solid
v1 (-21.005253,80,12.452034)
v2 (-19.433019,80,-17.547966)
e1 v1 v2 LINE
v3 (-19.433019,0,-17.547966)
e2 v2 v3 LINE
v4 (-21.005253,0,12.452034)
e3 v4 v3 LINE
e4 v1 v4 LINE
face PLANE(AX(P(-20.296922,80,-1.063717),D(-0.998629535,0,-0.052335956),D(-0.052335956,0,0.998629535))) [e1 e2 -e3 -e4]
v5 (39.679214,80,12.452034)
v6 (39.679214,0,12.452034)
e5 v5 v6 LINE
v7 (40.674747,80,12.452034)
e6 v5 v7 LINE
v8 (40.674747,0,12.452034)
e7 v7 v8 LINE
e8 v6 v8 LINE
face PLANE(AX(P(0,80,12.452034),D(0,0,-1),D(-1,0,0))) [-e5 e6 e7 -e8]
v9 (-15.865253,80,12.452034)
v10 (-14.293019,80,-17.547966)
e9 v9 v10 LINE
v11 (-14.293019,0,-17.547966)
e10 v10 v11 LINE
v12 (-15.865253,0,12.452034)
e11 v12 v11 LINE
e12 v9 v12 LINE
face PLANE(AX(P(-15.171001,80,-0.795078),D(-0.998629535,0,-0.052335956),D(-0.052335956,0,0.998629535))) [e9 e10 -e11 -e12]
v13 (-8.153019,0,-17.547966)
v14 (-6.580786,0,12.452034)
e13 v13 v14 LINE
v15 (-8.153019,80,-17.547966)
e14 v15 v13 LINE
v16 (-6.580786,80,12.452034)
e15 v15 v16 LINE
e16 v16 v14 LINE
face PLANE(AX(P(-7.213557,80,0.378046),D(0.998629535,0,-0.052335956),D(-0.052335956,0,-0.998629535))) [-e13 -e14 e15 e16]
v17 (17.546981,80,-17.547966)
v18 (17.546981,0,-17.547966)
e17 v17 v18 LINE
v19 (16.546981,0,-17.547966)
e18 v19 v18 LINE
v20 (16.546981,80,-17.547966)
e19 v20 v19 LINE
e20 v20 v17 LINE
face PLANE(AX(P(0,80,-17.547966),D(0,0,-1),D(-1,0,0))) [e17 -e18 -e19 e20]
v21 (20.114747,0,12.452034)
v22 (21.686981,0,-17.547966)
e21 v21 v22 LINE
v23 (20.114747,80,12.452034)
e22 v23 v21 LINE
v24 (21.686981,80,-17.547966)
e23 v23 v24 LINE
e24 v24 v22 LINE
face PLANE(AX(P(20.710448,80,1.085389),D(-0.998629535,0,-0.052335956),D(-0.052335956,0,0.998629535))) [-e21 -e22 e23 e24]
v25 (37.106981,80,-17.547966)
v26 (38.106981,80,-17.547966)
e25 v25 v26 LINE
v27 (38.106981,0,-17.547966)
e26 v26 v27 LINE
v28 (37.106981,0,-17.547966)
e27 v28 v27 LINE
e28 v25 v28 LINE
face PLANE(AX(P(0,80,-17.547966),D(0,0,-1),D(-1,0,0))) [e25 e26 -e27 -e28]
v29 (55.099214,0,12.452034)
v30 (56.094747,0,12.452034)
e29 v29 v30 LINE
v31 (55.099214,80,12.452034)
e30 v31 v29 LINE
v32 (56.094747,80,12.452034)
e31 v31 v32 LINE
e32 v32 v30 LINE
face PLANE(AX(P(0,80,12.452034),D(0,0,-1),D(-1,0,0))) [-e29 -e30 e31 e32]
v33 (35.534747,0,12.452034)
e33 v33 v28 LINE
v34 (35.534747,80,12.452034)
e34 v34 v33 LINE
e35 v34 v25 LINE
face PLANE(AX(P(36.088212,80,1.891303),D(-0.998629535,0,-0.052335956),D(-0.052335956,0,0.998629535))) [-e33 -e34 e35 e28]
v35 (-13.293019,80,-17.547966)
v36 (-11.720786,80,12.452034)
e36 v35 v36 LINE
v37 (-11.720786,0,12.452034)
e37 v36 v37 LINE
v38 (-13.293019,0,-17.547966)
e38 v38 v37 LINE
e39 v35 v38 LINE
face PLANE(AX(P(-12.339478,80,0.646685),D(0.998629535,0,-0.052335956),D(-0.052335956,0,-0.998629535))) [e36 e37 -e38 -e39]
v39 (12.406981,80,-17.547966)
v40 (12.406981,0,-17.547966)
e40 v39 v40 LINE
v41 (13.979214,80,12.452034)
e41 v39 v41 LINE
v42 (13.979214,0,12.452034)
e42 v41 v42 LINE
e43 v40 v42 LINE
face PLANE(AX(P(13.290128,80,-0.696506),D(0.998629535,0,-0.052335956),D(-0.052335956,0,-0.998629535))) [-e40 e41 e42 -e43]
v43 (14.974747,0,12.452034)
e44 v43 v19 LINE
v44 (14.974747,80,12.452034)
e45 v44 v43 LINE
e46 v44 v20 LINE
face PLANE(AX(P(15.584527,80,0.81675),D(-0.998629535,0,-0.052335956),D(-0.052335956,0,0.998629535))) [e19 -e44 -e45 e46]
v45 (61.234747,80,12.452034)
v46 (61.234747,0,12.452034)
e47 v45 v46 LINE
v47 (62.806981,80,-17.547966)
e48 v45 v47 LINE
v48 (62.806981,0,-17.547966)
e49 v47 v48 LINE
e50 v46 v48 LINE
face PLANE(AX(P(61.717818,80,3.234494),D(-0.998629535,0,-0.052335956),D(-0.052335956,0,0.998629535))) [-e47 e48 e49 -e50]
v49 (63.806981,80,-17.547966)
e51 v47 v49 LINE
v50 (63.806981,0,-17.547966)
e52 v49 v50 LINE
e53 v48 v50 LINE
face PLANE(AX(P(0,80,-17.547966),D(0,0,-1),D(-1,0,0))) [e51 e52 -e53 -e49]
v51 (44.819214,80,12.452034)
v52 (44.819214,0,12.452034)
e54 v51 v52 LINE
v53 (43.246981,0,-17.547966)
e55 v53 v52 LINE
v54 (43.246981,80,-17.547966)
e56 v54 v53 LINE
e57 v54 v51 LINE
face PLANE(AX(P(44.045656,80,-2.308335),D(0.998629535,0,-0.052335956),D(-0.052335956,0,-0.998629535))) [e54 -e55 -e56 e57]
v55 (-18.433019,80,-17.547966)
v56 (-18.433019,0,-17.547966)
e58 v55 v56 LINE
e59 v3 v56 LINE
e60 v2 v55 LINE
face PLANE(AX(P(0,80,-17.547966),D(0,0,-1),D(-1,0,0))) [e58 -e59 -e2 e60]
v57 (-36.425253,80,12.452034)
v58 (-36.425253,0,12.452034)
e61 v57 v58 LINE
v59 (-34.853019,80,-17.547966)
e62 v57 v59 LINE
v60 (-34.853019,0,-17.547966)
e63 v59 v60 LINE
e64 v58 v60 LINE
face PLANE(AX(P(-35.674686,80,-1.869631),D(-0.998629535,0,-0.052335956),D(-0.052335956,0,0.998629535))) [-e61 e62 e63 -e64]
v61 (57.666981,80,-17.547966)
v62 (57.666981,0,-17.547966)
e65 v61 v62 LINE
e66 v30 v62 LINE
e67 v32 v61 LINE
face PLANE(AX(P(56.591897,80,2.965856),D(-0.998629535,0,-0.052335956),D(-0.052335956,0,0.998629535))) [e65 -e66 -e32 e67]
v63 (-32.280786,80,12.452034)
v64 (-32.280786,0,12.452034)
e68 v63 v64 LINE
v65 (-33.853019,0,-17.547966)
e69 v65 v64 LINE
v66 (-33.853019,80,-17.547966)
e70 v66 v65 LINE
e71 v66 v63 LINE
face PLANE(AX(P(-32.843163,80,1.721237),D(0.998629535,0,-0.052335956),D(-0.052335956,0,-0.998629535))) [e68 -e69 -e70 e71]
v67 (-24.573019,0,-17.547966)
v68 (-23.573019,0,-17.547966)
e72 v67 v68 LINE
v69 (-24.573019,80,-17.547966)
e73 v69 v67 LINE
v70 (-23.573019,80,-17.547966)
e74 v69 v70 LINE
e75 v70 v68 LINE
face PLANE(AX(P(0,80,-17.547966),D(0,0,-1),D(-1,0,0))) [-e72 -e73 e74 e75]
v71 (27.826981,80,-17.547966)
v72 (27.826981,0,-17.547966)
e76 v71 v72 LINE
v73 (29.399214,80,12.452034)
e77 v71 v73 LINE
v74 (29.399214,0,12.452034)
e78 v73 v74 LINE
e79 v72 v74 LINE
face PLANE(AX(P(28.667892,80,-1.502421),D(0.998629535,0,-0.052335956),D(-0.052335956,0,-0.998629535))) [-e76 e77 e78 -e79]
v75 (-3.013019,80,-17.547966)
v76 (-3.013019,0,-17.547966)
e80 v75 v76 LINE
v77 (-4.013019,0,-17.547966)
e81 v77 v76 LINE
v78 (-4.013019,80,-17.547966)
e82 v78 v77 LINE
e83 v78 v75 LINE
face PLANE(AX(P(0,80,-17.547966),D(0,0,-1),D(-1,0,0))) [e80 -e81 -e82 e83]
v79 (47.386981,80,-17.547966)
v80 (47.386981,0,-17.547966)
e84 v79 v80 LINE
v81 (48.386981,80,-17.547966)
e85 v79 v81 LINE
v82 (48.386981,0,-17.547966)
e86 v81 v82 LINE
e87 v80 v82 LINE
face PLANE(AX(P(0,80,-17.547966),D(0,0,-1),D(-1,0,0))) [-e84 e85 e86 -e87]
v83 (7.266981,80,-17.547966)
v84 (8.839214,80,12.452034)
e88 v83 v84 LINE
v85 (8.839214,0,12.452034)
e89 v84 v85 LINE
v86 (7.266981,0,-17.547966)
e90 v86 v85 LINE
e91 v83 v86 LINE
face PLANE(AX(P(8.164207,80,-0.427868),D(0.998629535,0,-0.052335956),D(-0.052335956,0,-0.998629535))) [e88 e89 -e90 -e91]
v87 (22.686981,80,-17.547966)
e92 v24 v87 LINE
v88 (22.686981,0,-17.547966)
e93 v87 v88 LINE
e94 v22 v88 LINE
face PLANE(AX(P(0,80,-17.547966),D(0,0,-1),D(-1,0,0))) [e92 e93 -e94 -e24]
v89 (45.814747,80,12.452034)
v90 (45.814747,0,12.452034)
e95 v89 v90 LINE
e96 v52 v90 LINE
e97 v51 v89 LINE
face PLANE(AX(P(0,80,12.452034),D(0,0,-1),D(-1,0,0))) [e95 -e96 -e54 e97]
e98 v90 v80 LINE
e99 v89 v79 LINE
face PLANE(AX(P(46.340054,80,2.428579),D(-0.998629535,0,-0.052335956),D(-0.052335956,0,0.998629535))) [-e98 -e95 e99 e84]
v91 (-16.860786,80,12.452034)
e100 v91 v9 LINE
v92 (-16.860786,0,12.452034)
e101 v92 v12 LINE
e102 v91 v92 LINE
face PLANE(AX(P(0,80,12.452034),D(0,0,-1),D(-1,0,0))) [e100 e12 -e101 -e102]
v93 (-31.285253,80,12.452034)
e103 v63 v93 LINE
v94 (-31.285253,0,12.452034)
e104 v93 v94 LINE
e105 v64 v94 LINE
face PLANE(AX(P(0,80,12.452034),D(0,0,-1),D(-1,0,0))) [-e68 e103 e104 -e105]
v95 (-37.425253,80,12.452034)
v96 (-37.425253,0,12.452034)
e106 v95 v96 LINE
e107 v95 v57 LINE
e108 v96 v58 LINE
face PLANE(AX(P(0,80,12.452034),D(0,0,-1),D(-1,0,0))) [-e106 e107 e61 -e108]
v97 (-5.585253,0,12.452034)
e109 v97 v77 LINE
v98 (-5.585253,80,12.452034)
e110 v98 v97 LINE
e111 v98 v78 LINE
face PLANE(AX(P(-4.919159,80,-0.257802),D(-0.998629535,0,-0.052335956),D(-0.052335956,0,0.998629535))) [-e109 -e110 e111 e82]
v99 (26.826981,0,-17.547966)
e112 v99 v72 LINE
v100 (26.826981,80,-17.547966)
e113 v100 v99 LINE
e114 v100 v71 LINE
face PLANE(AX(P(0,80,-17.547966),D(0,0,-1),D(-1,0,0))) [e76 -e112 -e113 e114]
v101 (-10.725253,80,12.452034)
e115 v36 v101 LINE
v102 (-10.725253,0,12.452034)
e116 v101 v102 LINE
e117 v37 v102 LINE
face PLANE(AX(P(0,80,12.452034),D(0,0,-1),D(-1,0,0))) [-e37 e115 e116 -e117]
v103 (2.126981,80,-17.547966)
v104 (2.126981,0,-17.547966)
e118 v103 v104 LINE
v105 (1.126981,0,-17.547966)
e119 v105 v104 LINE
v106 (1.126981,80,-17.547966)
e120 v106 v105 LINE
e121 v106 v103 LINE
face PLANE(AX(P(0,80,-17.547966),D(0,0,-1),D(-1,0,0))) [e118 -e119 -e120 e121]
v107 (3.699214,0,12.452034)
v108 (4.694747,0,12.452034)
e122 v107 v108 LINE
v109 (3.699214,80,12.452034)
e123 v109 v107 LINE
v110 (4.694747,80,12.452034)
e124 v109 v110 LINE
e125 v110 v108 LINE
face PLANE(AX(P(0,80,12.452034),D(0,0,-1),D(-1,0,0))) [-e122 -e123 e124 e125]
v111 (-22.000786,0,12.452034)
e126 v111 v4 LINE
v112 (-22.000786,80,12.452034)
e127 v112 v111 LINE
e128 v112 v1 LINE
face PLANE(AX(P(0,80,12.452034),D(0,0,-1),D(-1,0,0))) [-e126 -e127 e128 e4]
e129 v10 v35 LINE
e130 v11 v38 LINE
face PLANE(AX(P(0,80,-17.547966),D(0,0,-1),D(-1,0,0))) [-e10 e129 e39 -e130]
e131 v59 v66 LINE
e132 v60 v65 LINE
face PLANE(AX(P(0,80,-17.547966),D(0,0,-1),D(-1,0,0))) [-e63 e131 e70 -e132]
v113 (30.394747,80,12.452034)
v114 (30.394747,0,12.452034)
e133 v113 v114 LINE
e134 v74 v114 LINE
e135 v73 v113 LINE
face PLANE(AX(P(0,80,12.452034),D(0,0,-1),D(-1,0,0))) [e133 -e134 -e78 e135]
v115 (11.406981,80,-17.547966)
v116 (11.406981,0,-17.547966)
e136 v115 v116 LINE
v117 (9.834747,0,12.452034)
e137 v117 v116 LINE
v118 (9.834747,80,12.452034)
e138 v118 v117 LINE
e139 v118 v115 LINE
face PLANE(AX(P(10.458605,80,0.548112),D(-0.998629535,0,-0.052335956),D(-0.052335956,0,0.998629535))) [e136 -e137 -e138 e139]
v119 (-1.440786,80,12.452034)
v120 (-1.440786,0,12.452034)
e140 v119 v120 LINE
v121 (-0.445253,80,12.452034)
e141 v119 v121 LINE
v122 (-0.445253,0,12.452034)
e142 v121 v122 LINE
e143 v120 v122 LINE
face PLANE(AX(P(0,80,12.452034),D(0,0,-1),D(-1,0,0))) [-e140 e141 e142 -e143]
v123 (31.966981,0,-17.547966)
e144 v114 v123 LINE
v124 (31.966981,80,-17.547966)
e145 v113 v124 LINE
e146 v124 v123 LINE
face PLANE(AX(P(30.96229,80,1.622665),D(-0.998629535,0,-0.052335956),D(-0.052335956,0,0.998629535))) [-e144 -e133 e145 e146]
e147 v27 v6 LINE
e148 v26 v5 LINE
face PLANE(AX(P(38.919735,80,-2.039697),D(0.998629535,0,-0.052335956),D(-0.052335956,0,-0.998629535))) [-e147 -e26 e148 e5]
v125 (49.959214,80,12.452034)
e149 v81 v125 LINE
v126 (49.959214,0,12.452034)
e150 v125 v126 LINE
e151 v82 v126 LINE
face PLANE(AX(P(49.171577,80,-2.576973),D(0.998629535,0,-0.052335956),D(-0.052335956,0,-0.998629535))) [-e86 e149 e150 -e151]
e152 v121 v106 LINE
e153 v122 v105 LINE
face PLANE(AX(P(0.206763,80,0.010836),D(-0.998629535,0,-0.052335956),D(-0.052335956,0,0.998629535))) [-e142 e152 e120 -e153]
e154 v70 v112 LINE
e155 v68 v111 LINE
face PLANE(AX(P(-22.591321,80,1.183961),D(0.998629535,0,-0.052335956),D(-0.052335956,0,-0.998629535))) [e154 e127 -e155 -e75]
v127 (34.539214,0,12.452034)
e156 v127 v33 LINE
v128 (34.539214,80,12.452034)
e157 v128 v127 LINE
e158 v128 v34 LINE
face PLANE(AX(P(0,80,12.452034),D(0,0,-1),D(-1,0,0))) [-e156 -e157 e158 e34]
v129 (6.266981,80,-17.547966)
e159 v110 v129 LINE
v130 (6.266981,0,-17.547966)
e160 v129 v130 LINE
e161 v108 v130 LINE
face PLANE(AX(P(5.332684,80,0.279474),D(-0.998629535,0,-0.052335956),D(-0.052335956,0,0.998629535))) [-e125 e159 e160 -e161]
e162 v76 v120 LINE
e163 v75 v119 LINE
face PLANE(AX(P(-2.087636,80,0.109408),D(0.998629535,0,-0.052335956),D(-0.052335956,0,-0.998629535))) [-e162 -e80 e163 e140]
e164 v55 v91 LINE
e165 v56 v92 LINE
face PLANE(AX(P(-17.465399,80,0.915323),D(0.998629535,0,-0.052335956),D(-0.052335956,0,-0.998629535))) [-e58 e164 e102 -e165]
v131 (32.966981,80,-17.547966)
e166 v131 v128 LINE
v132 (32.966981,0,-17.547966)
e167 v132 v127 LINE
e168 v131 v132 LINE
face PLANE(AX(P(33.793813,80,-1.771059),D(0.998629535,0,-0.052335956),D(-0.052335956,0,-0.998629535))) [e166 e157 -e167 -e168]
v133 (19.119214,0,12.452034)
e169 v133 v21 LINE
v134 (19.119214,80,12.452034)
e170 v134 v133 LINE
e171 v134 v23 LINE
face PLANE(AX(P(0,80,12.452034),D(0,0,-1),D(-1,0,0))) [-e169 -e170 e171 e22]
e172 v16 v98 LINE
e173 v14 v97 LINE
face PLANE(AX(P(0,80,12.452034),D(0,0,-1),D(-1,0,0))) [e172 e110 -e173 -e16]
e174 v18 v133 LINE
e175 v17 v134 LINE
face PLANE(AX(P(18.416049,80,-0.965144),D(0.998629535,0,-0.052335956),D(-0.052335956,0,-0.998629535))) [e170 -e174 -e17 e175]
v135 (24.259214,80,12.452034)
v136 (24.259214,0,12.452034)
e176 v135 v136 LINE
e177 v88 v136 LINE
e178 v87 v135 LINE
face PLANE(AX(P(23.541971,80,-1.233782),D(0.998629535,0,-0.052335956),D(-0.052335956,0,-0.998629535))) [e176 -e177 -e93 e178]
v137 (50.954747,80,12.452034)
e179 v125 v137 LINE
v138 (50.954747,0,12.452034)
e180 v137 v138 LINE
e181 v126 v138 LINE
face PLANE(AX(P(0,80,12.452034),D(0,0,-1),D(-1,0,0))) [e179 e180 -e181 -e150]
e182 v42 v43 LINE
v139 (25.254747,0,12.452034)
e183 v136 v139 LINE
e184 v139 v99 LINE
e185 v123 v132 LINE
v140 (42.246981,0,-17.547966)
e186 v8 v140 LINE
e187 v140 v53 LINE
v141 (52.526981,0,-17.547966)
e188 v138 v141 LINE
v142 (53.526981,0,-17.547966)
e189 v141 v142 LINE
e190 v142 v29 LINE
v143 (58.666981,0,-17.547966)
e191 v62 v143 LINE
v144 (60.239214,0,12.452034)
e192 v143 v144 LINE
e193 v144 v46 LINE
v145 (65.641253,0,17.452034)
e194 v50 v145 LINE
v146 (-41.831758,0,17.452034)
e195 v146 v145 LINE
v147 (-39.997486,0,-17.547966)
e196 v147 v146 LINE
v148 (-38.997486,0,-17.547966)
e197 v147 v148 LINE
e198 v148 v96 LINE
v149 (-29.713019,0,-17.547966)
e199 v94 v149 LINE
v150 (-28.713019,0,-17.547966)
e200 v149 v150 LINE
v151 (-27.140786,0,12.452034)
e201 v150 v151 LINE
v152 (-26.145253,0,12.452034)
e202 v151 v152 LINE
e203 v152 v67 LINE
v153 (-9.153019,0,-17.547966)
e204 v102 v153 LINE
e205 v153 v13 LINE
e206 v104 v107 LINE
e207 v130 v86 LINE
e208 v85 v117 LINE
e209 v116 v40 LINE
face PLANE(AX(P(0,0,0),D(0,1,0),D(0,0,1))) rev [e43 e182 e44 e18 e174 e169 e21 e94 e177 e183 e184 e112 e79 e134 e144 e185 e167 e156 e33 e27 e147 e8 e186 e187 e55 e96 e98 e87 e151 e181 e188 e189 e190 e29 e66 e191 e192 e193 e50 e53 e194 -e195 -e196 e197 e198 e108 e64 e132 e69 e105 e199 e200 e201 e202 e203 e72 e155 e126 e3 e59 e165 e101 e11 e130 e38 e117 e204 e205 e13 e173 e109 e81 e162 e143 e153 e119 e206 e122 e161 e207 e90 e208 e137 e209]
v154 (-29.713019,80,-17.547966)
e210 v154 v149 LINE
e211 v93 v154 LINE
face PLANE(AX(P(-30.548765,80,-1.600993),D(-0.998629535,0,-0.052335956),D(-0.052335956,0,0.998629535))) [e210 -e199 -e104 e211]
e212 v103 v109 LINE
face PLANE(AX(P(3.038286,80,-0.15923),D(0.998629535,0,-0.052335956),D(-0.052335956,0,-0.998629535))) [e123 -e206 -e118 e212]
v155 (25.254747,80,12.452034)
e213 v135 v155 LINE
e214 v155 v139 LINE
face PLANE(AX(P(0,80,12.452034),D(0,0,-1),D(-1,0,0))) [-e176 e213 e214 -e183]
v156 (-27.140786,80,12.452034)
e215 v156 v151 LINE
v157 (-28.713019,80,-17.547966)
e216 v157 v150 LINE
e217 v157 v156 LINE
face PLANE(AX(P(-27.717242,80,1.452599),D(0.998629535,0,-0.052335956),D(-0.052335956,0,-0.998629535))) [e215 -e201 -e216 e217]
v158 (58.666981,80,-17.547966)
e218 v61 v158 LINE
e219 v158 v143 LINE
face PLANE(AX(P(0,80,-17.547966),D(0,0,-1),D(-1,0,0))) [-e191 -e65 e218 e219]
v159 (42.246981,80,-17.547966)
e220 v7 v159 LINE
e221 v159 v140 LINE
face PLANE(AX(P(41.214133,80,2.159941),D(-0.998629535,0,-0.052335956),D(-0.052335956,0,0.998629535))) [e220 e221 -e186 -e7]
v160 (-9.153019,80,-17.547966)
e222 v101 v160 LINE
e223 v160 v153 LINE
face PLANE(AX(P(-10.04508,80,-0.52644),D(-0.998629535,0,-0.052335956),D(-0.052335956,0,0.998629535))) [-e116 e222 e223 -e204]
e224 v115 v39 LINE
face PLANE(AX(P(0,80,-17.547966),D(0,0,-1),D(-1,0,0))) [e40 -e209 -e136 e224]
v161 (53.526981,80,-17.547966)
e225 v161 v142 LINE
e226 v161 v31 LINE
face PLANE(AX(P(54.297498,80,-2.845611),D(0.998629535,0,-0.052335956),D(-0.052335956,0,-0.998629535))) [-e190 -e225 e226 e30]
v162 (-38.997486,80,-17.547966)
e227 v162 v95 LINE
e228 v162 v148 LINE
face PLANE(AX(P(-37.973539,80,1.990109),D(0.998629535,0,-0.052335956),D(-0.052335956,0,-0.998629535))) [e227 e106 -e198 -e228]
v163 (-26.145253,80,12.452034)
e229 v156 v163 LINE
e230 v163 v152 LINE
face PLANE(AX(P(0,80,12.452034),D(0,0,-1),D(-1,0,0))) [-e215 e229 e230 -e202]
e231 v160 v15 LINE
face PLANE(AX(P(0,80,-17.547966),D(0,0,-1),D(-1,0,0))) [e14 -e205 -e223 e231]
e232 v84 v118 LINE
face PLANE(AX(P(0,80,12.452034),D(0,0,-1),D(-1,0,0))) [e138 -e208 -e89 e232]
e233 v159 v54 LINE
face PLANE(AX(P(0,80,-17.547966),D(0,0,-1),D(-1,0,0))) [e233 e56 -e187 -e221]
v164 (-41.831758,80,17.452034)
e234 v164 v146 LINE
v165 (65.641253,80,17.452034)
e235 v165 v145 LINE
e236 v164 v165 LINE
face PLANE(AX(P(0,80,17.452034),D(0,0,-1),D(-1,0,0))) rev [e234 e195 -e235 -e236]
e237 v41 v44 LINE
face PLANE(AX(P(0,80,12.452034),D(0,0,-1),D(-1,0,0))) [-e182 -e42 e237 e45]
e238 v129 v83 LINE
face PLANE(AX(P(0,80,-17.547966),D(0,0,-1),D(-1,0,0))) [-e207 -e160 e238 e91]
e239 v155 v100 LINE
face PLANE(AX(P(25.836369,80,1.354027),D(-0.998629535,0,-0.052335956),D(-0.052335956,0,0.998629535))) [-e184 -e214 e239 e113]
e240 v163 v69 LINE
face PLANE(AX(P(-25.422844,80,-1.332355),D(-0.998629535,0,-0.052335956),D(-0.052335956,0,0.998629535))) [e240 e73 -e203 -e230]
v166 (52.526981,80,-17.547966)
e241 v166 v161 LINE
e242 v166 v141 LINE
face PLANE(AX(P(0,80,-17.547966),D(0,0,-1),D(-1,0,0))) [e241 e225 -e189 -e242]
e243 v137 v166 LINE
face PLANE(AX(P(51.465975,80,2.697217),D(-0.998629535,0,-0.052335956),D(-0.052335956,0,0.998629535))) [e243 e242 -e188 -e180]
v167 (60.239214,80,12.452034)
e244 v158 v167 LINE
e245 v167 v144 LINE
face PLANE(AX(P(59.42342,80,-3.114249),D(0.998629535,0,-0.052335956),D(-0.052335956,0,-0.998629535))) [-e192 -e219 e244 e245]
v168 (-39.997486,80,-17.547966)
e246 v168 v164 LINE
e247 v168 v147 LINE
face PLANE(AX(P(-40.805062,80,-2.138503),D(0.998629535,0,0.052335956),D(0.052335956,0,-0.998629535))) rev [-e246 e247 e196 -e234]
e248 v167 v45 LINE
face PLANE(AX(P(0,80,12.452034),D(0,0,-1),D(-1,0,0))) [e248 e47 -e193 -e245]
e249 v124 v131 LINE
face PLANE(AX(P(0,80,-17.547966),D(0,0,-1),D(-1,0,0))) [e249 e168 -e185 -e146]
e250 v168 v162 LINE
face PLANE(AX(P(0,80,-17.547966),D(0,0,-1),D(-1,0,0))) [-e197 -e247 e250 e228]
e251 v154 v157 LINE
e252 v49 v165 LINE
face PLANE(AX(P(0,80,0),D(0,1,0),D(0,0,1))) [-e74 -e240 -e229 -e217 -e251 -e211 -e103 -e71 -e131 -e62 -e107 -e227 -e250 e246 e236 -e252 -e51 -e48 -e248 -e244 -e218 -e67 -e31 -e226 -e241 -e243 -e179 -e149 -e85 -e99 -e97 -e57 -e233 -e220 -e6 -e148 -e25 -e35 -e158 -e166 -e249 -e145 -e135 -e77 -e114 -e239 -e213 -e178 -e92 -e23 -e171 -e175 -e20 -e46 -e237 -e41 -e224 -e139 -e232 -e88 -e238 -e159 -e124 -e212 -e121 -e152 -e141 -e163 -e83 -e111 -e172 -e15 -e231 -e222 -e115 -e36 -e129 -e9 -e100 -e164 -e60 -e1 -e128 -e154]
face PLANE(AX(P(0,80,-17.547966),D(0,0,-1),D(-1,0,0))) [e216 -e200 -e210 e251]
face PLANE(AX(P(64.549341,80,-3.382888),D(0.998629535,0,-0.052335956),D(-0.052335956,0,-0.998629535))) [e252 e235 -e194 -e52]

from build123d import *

# Parameters (mm, degrees)
HEAT_SINK_BODY_EXTRUDE_80MM_DEPTH = 80


with BuildPart() as part:
    # Heat Sink Profile 20 Fins → Heat Sink Body Extrude 80mm (new body)
    with BuildSketch(Plane(origin=(0, 0, 0), x_dir=(1, 0, 0), z_dir=(0, 1, 0))):
        Polygon((-38.997486194, 17.547966284), (-39.997486194, 17.547966284), (-41.831758469, -17.452033716), (65.641252838, -17.452033716), (63.806980563, 17.547966284), (62.806980563, 17.547966284), (61.234747185, -12.452033716), (60.239213942, -12.452033716), (58.666980563, 17.547966284), (57.666980563, 17.547966284), (56.094747185, -12.452033716), (55.099213942, -12.452033716), (53.526980563, 17.547966284), (52.526980563, 17.547966284), (50.954747185, -12.452033716), (49.959213942, -12.452033716), (48.386980563, 17.547966284), (47.386980563, 17.547966284), (45.814747185, -12.452033716), (44.819213942, -12.452033716), (43.246980563, 17.547966284), (42.246980563, 17.547966284), (40.674747185, -12.452033716), (39.679213942, -12.452033716), (38.106980563, 17.547966284), (37.106980563, 17.547966284), (35.534747185, -12.452033716), (34.539213942, -12.452033716), (32.966980563, 17.547966284), (31.966980563, 17.547966284), (30.394747185, -12.452033716), (29.399213942, -12.452033716), (27.826980563, 17.547966284), (26.826980563, 17.547966284), (25.254747185, -12.452033716), (24.259213942, -12.452033716), (22.686980563, 17.547966284), (21.686980563, 17.547966284), (20.114747185, -12.452033716), (19.119213942, -12.452033716), (17.546980563, 17.547966284), (16.546980563, 17.547966284), (14.974747185, -12.452033716), (13.979213942, -12.452033716), (12.406980563, 17.547966284), (11.406980563, 17.547966284), (9.834747185, -12.452033716), (8.839213942, -12.452033716), (7.266980563, 17.547966284), (6.266980563, 17.547966284), (4.694747185, -12.452033716), (3.699213942, -12.452033716), (2.126980563, 17.547966284), (1.126980563, 17.547966284), (-0.445252815, -12.452033716), (-1.440786058, -12.452033716), (-3.013019437, 17.547966284), (-4.013019437, 17.547966284), (-5.585252815, -12.452033716), (-6.580786058, -12.452033716), (-8.153019437, 17.547966284), (-9.153019437, 17.547966284), (-10.725252815, -12.452033716), (-11.720786058, -12.452033716), (-13.293019437, 17.547966284), (-13.392304127, 17.547966284), (-14.293019437, 17.547966284), (-15.865252815, -12.452033716), (-16.860786058, -12.452033716), (-18.433019437, 17.547966284), (-19.433019437, 17.547966284), (-21.005252815, -12.452033716), (-22.000786058, -12.452033716), (-23.573019437, 17.547966284), (-24.573019437, 17.547966284), (-26.145252815, -12.452033716), (-27.140786058, -12.452033716), (-28.713019437, 17.547966284), (-29.713019437, 17.547966284), (-31.285252815, -12.452033716), (-32.280786058, -12.452033716), (-33.853019437, 17.547966284), (-34.853019437, 17.547966284), (-36.425252815, -12.452033716), (-37.425252815, -12.452033716), align=None)
    extrude(amount=HEAT_SINK_BODY_EXTRUDE_80MM_DEPTH)


solid = part.part
